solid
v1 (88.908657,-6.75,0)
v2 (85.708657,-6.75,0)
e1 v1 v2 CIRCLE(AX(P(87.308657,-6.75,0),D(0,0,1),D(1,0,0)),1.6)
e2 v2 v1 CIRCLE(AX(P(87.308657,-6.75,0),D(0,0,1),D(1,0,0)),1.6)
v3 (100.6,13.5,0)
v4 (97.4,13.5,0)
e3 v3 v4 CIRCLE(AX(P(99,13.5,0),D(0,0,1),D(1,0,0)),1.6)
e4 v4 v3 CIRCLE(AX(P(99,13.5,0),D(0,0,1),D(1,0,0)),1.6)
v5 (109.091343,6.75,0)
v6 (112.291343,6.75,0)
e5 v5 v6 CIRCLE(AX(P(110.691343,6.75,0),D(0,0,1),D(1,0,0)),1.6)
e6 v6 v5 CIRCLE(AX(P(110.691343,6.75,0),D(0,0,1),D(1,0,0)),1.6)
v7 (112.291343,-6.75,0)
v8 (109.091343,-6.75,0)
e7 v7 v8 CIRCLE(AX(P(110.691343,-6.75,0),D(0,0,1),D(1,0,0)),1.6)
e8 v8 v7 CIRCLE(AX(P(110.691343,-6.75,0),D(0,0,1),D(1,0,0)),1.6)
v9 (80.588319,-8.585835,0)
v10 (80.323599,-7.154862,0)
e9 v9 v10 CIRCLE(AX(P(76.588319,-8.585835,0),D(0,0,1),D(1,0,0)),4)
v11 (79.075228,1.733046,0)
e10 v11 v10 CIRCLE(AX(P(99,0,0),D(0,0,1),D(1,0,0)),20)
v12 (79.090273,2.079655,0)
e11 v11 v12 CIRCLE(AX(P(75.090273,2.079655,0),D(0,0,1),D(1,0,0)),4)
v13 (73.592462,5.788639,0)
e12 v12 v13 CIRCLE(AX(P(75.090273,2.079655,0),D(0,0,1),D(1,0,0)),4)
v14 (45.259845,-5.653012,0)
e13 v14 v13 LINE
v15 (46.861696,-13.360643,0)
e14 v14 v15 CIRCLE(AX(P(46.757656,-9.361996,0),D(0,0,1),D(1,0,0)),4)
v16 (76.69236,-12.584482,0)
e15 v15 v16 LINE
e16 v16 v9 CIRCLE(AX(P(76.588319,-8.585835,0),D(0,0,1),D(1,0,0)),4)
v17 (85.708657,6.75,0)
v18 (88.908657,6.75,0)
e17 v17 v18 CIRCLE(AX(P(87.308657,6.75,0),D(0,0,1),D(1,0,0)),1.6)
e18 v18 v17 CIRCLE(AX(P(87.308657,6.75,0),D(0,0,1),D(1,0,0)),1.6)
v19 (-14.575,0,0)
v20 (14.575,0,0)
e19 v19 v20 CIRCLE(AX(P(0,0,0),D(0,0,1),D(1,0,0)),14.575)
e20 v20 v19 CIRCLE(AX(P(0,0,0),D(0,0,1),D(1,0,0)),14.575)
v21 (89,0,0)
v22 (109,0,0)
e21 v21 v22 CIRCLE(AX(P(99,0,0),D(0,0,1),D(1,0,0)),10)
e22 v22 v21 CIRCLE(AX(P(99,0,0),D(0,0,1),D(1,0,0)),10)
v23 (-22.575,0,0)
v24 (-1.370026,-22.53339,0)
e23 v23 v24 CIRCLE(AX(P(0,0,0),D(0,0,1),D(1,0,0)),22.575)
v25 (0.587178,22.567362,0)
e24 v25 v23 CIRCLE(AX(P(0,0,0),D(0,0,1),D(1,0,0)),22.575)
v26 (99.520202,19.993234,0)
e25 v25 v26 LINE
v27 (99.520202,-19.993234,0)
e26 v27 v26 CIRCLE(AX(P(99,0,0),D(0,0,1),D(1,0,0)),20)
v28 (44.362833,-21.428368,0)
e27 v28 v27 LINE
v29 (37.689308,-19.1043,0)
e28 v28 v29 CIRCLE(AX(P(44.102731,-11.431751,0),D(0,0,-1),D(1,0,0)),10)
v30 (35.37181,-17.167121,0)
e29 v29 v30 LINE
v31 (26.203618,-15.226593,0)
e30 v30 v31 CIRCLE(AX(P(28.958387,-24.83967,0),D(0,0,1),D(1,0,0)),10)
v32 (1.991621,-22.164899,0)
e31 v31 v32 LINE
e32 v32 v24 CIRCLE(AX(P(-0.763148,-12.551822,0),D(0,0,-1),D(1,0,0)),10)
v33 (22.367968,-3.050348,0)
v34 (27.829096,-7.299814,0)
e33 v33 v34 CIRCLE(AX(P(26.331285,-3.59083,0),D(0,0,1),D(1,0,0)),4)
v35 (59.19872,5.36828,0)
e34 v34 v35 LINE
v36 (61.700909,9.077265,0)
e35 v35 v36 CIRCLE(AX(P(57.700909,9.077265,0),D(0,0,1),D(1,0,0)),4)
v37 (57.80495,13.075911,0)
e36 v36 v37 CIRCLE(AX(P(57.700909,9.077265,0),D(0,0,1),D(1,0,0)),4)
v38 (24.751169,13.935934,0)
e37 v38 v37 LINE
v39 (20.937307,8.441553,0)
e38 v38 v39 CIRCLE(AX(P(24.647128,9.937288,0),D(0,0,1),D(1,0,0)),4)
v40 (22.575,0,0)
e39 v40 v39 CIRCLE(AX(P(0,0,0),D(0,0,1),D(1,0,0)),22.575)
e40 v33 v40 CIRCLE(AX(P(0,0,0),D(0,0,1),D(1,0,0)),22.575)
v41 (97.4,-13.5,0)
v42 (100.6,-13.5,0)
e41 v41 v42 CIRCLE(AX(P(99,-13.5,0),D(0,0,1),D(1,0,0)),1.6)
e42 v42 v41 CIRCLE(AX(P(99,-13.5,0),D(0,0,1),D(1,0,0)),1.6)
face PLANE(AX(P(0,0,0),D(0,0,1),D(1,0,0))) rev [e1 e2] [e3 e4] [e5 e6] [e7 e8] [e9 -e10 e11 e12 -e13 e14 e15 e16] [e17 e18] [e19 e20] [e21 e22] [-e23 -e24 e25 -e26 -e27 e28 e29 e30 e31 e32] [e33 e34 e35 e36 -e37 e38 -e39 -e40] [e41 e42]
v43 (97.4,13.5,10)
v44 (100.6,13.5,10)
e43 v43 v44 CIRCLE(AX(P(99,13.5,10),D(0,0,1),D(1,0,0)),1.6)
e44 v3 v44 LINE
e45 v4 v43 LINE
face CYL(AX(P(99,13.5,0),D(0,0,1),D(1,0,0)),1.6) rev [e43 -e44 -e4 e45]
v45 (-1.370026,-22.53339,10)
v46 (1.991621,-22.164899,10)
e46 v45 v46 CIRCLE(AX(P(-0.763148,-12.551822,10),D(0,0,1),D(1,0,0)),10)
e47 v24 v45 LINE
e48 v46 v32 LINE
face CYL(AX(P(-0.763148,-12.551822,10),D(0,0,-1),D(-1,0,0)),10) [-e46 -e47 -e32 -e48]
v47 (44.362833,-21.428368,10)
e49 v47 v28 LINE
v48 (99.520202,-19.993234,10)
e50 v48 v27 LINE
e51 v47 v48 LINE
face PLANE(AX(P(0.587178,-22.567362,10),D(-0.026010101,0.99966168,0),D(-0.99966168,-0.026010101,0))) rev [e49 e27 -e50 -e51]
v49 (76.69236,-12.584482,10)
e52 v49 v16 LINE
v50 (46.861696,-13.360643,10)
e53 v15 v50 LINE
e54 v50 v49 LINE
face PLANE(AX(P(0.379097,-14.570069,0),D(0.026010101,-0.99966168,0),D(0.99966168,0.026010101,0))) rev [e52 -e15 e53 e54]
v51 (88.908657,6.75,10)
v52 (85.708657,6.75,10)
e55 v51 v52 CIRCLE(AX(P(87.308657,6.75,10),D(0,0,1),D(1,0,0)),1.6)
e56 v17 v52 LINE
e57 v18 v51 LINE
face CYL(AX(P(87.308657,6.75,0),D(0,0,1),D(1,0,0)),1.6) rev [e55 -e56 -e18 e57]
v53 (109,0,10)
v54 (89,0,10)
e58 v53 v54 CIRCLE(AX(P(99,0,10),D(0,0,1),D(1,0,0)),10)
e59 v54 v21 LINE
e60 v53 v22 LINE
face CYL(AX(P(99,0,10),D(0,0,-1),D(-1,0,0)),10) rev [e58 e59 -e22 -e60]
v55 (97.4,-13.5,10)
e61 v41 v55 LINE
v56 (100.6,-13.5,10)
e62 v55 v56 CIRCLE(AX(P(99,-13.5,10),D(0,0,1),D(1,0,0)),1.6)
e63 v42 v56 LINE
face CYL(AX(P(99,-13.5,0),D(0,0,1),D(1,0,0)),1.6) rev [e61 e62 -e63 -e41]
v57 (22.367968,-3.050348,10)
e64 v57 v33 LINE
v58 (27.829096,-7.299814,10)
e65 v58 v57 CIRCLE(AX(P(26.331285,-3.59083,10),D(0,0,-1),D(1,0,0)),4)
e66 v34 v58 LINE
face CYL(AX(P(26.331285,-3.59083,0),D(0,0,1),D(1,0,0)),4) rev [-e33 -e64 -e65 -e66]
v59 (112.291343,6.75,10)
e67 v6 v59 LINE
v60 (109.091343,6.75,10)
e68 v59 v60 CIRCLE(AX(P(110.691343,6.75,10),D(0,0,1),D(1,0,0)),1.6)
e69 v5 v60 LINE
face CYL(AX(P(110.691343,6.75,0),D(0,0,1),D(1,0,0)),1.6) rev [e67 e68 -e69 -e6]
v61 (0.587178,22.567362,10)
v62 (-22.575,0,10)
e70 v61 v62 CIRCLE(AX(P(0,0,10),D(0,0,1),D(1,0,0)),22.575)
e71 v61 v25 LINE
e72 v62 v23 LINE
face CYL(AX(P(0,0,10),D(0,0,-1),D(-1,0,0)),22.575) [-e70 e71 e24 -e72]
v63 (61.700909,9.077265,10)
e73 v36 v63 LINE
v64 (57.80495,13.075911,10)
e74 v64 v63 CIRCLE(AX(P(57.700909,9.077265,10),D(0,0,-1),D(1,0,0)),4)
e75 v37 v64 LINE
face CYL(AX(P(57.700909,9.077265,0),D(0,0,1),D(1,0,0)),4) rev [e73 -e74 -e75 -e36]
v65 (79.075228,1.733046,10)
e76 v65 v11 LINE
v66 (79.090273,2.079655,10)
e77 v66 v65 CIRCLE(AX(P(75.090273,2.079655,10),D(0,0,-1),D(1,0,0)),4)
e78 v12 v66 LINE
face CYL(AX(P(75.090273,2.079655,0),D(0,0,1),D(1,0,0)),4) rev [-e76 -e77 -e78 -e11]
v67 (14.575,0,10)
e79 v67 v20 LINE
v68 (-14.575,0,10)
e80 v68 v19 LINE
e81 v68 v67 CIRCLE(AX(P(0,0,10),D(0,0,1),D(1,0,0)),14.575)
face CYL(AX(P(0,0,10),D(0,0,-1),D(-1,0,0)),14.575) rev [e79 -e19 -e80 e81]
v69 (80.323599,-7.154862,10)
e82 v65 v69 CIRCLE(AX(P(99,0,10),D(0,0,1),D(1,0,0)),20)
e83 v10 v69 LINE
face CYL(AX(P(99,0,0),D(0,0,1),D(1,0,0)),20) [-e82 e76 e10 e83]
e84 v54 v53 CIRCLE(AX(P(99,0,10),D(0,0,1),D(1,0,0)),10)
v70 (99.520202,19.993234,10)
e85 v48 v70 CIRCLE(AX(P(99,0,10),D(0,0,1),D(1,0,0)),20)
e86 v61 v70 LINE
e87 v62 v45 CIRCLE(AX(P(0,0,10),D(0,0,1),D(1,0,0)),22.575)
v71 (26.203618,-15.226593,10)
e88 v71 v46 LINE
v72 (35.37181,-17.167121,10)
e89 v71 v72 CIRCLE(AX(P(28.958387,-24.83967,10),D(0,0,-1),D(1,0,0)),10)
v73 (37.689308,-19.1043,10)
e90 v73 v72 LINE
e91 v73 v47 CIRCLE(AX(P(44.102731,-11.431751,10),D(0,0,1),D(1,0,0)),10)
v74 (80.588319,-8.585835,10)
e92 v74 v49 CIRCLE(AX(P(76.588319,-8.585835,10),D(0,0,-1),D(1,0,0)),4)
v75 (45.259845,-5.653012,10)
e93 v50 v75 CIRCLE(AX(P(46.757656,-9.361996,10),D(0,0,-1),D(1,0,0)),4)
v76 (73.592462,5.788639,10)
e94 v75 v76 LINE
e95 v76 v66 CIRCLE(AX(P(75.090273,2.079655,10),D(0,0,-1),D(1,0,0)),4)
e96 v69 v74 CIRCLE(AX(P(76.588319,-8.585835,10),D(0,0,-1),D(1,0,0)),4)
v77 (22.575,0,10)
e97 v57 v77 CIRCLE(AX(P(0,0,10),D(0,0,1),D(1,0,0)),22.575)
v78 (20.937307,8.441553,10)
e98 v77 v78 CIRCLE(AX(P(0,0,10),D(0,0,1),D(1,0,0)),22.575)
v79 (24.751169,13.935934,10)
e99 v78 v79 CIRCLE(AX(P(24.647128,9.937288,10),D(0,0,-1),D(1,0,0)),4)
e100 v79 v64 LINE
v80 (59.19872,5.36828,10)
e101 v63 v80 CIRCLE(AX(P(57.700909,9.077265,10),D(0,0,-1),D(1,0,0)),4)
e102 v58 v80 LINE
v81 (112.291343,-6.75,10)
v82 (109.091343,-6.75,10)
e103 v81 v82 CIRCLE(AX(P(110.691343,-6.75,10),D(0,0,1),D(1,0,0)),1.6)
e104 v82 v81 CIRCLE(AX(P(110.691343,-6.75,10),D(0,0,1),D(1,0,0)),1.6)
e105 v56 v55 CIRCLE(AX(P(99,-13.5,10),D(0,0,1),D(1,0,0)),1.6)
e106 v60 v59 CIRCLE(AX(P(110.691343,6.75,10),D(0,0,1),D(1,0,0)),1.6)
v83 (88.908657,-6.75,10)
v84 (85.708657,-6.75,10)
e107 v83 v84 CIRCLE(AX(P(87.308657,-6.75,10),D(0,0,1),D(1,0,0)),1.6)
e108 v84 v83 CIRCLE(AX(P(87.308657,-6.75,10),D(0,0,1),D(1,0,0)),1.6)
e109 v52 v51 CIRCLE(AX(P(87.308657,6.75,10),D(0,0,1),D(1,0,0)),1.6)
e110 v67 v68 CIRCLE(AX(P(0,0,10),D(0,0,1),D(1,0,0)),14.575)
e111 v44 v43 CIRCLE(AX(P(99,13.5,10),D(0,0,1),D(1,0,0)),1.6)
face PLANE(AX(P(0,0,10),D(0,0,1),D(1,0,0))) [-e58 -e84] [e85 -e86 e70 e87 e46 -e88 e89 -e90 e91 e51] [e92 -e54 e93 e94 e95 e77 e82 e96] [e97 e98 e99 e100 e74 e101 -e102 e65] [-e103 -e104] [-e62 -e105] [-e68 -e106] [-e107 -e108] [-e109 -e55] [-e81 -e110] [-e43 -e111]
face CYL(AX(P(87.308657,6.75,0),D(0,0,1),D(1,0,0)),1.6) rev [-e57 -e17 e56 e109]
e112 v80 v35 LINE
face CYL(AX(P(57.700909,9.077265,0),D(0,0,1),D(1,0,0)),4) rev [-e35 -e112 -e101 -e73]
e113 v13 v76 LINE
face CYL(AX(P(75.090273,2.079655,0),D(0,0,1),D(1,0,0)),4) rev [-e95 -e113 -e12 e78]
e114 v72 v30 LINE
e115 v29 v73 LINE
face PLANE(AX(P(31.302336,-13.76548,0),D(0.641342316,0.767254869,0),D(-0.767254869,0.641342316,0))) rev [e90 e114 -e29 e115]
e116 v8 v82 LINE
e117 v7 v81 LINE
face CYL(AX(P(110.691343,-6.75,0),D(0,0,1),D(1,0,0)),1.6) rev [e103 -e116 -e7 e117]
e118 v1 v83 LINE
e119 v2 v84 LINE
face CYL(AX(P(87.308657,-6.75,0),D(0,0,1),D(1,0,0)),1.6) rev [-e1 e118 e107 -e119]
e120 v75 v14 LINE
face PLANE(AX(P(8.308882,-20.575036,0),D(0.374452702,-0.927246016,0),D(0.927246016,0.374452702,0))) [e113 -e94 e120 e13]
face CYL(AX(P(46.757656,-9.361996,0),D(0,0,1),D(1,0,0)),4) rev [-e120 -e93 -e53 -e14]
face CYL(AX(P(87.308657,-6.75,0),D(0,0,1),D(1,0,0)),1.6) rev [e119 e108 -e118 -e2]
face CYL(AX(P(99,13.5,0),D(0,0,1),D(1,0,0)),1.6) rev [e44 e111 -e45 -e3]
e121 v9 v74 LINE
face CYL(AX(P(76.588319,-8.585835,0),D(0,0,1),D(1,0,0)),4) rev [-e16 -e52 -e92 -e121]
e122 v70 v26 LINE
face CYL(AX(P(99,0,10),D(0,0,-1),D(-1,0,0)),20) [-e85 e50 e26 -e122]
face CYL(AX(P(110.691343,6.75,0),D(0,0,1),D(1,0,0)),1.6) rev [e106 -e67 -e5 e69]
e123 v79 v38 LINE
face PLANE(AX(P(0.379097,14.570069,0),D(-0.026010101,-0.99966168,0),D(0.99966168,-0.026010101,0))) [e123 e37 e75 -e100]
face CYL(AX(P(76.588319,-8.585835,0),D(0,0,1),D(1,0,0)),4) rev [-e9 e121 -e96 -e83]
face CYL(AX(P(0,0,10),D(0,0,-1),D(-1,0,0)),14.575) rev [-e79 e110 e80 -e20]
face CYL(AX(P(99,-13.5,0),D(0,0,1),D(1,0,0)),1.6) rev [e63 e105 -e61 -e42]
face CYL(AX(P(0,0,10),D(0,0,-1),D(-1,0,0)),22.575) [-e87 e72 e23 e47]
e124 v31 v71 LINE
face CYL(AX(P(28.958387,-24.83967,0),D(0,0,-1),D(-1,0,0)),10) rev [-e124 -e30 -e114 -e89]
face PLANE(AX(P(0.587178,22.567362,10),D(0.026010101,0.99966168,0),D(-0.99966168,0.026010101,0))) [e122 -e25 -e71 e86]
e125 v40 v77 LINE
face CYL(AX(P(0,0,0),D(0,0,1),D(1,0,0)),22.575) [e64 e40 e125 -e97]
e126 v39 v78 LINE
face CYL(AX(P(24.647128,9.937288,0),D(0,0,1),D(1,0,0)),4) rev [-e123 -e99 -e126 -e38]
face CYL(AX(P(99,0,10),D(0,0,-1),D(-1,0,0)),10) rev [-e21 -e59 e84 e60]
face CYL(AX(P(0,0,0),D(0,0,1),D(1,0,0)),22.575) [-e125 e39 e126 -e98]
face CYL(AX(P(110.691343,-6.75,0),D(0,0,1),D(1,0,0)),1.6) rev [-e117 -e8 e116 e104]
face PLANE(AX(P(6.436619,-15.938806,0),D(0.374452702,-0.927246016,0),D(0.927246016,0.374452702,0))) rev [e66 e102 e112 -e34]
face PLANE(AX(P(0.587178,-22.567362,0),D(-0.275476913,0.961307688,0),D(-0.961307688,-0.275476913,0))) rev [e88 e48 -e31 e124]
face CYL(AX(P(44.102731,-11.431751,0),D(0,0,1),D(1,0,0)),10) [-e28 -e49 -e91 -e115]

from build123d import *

# Parameters (mm, degrees)
SKETCH_1_R          = 14.575
SKETCH_1_R_2        = 10
EXTRUDE_1_DEPTH     = 10
CUT_EXTRUDE_START   = -10
CUT_EXTRUDE_1_DEPTH = 10
FILLET_1_R          = 4
SKETCH_3_R          = 1.6
CUT_EXTRUDE_2_DEPTH = 10
CUT_EXTRUDE_3_DEPTH = 10
FILLET_2_R          = 10


with BuildPart() as part:
    # 草图1 → 凸台-拉伸1 (new body)
    with BuildSketch(Plane.XY):
        with BuildLine():
            ThreePointArc((0.58717803, 22.567362428), (-22.575, 0), (0.58717803, -22.567362428))
            Line((0.58717803, -22.567362428), (99.52020202, -19.993233602))
            ThreePointArc((99.52020202, -19.993233602), (119, 0), (99.52020202, 19.993233602))
            Line((99.52020202, 19.993233602), (0.58717803, 22.567362428))
        make_face()
        Circle(SKETCH_1_R, mode=Mode.SUBTRACT)
        with Locations((99, 0)):
            Circle(SKETCH_1_R_2, mode=Mode.SUBTRACT)
    extrude(amount=EXTRUDE_1_DEPTH)

    # 草图2 → 切除-拉伸1 (cut)
    with BuildSketch(Plane.XY.offset(10).offset(CUT_EXTRUDE_START)):
        with BuildLine():
            Line((77.045246178, 12.575299839), (17.612754311, 14.121668123))
            ThreePointArc((17.612754311, 14.121668123), (21.298339766, 7.484072969), (22.575, 0))
            ThreePointArc((22.575, 0), (21.923337, -5.384971659), (20.005970563, -10.459051908))
            Line((20.005970563, -10.459051908), (77.045246178, 12.575299839))
        make_face()
        with BuildLine():
            Line((81.037736343, 8.795287621), (24.748948749, -13.935992167))
            Line((24.748948749, -13.935992167), (83.317534331, -12.412101777))
            ThreePointArc((83.317534331, -12.412101777), (79.114570809, -2.137687039), (81.037736343, 8.795287621))
        make_face()
    extrude(amount=CUT_EXTRUDE_1_DEPTH, mode=Mode.SUBTRACT)

    # 圆角1
    fillet_1_edges = [part.edges().sort_by_distance(p)[0] for p in [
        (81.037736343, 8.795287621, 5),
        (83.317534331, -12.412101777, 5),
        (24.748948749, -13.935992167, 5),
        (20.005970563, -10.459051908, 5),
        (17.612754311, 14.121668123, 5),
        (77.045246178, 12.575299839, 5),
    ]]
    fillet(fillet_1_edges, radius=FILLET_1_R)

    # 草图3 → 切除-拉伸2 (cut)
    with BuildSketch(Plane.XY.offset(10)):
        with Locations((99, 13.5)):
            Circle(SKETCH_3_R)
        with Locations((110.691342951, 6.75)):
            Circle(SKETCH_3_R)
        with Locations((110.691342951, -6.75)):
            Circle(SKETCH_3_R)
        with Locations((99, -13.5)):
            Circle(SKETCH_3_R)
        with Locations((87.308657049, -6.75)):
            Circle(SKETCH_3_R)
        with Locations((87.308657049, 6.75)):
            Circle(SKETCH_3_R)
    extrude(amount=-CUT_EXTRUDE_2_DEPTH, mode=Mode.SUBTRACT)

    # 草图4 → 切除-拉伸3 (cut)
    with BuildSketch(Plane.XY.offset(10)):
        Polygon((0.58717803, -22.567362428), (31.302336493, -13.765480202), (40.58717803, -21.526606279), align=None)
    extrude(amount=-CUT_EXTRUDE_3_DEPTH, mode=Mode.SUBTRACT)

    # 圆角2
    fillet_2_edges = [part.edges().sort_by_distance(p)[0] for p in [
        (0.58717803, -22.567362428, 5),
        (40.58717803, -21.526606279, 5),
        (31.302336493, -13.765480202, 5),
    ]]
    fillet(fillet_2_edges, radius=FILLET_2_R)


solid = part.part
